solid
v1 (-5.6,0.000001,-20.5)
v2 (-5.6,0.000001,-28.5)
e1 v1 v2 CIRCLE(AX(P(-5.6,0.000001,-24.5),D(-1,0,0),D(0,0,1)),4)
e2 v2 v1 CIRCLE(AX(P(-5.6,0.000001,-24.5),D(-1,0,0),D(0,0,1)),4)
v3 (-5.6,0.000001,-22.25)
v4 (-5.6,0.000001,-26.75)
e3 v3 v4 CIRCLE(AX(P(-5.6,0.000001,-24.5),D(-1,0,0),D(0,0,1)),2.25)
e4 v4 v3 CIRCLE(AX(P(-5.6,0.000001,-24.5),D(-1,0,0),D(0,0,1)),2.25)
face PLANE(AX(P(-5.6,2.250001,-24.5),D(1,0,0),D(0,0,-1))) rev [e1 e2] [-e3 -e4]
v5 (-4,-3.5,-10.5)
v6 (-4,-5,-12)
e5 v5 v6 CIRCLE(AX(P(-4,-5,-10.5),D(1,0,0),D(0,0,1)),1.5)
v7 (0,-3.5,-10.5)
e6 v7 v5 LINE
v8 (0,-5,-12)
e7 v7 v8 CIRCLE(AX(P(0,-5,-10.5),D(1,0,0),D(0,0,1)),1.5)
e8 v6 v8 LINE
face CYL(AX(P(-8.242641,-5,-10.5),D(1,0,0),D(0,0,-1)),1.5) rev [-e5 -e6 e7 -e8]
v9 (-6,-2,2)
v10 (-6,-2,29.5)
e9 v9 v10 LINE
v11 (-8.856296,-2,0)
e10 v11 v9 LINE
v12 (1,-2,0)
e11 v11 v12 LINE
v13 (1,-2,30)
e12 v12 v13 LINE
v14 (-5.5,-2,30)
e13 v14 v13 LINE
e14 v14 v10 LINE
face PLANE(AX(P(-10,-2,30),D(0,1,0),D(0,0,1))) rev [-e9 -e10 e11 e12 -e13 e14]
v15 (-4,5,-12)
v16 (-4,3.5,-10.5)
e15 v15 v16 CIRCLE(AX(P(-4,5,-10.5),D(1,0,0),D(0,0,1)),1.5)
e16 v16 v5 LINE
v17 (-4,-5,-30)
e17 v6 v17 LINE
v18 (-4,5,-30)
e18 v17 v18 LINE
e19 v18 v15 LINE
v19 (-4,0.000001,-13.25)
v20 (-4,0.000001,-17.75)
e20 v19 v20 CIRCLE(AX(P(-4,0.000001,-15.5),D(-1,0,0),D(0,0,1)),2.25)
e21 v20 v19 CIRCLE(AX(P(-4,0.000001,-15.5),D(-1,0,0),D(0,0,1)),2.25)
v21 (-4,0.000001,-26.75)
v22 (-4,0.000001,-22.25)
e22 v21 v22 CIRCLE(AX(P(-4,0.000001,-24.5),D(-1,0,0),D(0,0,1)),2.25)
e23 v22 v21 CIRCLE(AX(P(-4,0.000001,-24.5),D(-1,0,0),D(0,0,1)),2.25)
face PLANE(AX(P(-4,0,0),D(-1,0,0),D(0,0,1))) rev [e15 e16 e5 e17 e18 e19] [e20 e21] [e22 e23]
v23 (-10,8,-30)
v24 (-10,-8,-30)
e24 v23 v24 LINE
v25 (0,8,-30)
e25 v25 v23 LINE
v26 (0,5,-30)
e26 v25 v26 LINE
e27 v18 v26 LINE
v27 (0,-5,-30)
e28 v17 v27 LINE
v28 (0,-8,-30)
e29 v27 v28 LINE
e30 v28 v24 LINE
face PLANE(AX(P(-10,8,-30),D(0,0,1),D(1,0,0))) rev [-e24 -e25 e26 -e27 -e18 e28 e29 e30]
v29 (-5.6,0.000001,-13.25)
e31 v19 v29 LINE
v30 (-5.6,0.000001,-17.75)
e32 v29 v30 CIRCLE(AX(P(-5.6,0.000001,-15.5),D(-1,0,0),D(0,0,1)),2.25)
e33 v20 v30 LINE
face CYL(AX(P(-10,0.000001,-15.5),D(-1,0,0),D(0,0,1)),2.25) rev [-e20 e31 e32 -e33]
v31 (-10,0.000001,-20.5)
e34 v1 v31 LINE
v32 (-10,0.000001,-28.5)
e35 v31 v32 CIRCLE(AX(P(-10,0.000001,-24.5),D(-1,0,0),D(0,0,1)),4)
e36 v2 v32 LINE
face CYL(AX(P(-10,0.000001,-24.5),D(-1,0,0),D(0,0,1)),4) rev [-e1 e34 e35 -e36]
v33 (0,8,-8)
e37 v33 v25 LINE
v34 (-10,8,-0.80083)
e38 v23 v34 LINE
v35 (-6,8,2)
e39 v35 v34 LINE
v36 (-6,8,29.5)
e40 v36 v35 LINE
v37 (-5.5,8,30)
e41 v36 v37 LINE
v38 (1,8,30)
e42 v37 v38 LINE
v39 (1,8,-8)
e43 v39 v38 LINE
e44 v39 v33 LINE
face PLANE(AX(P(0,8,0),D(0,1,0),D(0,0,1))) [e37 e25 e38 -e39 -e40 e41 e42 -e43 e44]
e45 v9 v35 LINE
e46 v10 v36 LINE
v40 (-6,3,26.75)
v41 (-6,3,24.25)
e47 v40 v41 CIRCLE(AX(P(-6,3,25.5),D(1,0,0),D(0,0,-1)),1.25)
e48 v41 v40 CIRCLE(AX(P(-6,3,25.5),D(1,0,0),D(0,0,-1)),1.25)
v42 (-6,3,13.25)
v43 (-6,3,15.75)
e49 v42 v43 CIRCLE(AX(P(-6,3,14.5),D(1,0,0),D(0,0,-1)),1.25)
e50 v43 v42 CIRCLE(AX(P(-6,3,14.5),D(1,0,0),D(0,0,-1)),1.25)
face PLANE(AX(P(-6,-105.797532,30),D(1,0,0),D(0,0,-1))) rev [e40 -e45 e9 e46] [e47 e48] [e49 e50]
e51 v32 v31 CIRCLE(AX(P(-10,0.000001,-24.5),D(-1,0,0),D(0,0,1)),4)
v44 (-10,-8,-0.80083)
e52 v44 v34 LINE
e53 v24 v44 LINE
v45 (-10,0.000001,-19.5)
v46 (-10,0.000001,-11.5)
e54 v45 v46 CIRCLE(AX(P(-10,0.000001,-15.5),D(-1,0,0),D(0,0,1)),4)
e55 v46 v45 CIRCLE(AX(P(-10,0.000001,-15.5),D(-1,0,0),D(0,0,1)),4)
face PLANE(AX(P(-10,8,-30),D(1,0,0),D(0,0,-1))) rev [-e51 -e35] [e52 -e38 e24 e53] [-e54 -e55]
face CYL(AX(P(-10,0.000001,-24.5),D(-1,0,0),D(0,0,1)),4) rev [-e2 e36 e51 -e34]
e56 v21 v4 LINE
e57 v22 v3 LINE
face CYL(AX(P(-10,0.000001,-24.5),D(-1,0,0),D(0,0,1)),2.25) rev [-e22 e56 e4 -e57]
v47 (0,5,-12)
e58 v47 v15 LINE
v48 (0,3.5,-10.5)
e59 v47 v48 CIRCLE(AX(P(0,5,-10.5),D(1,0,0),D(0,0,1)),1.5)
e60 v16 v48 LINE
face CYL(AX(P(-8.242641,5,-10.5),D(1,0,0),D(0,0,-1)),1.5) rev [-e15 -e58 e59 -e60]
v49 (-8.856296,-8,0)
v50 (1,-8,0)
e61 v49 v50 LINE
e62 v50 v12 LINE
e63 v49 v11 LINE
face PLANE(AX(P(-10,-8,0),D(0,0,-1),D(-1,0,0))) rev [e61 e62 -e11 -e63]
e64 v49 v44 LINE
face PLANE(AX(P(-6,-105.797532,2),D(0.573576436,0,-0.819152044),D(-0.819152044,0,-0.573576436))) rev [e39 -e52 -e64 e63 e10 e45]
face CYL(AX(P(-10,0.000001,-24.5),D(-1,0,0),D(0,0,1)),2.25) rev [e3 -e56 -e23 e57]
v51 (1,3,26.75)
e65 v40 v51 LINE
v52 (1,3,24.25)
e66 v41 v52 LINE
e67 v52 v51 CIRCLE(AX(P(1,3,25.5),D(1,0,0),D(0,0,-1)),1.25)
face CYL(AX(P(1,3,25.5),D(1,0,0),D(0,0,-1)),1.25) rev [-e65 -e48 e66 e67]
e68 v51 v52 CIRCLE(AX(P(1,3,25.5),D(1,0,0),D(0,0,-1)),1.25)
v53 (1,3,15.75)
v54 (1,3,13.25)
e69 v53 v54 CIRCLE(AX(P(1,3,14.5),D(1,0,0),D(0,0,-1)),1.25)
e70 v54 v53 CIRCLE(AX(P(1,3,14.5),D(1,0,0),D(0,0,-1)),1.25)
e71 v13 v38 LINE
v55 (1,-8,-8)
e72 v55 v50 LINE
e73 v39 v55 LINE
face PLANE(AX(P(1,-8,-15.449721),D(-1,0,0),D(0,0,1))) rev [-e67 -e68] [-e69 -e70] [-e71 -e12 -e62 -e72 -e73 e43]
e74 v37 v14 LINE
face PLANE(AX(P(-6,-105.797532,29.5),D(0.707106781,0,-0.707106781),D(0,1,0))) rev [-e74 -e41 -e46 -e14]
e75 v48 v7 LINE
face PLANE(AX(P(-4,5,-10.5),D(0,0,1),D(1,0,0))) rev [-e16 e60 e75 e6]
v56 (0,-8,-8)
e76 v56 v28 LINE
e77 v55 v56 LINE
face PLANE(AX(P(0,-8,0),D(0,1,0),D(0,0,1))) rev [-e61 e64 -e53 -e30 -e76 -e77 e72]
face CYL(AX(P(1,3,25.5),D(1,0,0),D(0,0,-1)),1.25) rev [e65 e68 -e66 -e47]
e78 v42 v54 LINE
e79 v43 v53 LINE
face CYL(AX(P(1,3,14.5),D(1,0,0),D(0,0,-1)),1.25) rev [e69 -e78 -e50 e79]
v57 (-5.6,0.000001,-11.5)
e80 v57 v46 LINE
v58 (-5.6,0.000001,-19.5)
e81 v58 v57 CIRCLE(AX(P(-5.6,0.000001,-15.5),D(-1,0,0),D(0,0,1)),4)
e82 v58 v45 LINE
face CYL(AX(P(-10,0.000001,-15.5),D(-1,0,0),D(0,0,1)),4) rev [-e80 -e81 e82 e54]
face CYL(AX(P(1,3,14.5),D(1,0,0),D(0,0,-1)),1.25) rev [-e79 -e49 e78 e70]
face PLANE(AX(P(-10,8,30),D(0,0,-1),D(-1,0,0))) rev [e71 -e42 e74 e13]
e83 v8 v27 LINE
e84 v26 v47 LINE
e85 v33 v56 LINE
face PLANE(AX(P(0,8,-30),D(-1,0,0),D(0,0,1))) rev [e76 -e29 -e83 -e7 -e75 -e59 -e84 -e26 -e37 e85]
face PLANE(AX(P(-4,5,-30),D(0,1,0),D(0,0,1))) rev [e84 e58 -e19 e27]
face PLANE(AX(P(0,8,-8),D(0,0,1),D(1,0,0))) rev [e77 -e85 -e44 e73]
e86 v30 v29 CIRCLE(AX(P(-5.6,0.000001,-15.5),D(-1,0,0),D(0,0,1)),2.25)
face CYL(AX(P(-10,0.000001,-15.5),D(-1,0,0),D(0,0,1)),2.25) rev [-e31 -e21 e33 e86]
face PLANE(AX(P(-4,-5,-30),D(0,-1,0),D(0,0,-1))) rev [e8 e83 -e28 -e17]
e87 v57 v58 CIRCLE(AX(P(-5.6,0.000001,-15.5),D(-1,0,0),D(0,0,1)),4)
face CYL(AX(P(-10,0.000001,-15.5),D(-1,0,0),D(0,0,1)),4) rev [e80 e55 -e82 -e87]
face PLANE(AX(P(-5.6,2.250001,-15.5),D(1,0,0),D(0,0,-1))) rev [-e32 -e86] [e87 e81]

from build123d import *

# Parameters (mm, degrees)
SKETCH_1_W                   = 20
SKETCH_1_H                   = 60
EXTRUDE_1_DEPTH              = 8
SKETCH_2_W                   = 19.5
SKETCH_2_H                   = 10
CUT_EXTRUDE_1_DEPTH          = 14
CHAMFER_1_SIZE               = 3
CUT_EXTRUDE_3_DEPTH          = 36.440090293
CUT_EXTRUDE_3_DEPTH_BACK     = 36.440090293
CHAMFER_2_SIZE               = 0.5
SKETCH_6_R                   = 1.5
CUT_EXTRUDE_4_DEPTH          = 14
HOLE_WIZARD_M4_1_D           = 4.5
HOLE_WIZARD_M4_1_CBORE_D     = 8
HOLE_WIZARD_M4_1_CBORE_DEPTH = 4.4
SKETCH_11_W                  = 10
SKETCH_11_H                  = 22
CUT_EXTRUDE_7_DEPTH          = 36.440090293
SKETCH_12_W                  = 30
SKETCH_12_H                  = 6
CUT_EXTRUDE_8_DEPTH          = 37.932370625
CUT_EXTRUDE_9_DEPTH          = 34.166247904
FILLET_2_R                   = 3
SKETCH_14_W                  = 18.511605667
SKETCH_14_H                  = 56.283608206
CUT_EXTRUDE_10_DEPTH         = 36.440090293
HOLE_WIZARD_M3_1_D           = 2.5


with BuildPart() as part:
    # 草图1 → 凸台-拉伸1 (new, symmetric)
    with BuildSketch(Plane(origin=(0, 0, 0), x_dir=(1, 0, 0), z_dir=(0, 1, 0))):
        Rectangle(SKETCH_1_W, SKETCH_1_H)
    extrude(amount=EXTRUDE_1_DEPTH, both=True)

    # 草图2 → 切除-拉伸1 (cut)
    with BuildSketch(Plane(origin=(10, 0, 0), x_dir=(0, 0, -1), z_dir=(1, 0, 0))):
        with Locations((20.25, 0)):
            Rectangle(SKETCH_2_W, SKETCH_2_H)
    extrude(amount=-CUT_EXTRUDE_1_DEPTH, mode=Mode.SUBTRACT)

    # 倒角1
    chamfer_1_edges = [part.edges().sort_by_distance(p)[0] for p in [
        (10, -6.5, -30),
        (10, 6.5, -30),
    ]]
    chamfer(chamfer_1_edges, length=CHAMFER_1_SIZE)

    # 草图5 → 切除-拉伸3 (cut, two sides: drawn at the far end of the back side and taken through both)
    with BuildSketch(Plane.XZ.offset(8).offset(-CUT_EXTRUDE_3_DEPTH_BACK)):
        Polygon((-6, 164.19339757), (-6, 30), (-6, 2), (-10, -0.800830153), (-119.92479595, -77.771000913), (-362.743295595, 36.555933952), (-248.818499645, 278.520332435), align=None)
    extrude(amount=CUT_EXTRUDE_3_DEPTH + CUT_EXTRUDE_3_DEPTH_BACK, mode=Mode.SUBTRACT)

    # 倒角2
    chamfer_2_edges = [part.edges().sort_by_distance(p)[0] for p in [
        (-6, 0, 30),
        (10, 0, 30),
    ]]
    chamfer(chamfer_2_edges, length=CHAMFER_2_SIZE)

    # 草图6 → 切除-拉伸4 (cut)
    with BuildSketch(Plane(origin=(10, 0, 0), x_dir=(0, 0, -1), z_dir=(1, 0, 0))):
        with Locations((10.5, 5)):
            Circle(SKETCH_6_R)
        with Locations((10.5, -5)):
            Circle(SKETCH_6_R)
    extrude(amount=-CUT_EXTRUDE_4_DEPTH, mode=Mode.SUBTRACT)

    # M4 六角凹头螺钉的柱形沉头孔1 (through all)
    with Locations(Plane.ZY.offset(10)):
        with Locations((-15.500000304, 6.53e-07), (-24.500000304, 6.53e-07)):
            CounterBoreHole(HOLE_WIZARD_M4_1_D / 2, HOLE_WIZARD_M4_1_CBORE_D / 2, HOLE_WIZARD_M4_1_CBORE_DEPTH)

    # 草图11 → 切除-拉伸7 (cut, through all)
    with BuildSketch(Plane.XZ.offset(8)):
        with Locations((5, -19)):
            Rectangle(SKETCH_11_W, SKETCH_11_H)
    extrude(amount=-CUT_EXTRUDE_7_DEPTH, mode=Mode.SUBTRACT)

    # 草图12 → 切除-拉伸8 (cut, through all)
    with BuildSketch(Plane(origin=(10, 0, 0), x_dir=(0, 0, -1), z_dir=(1, 0, 0))):
        with Locations((-15, -5)):
            Rectangle(SKETCH_12_W, SKETCH_12_H)
    extrude(amount=-CUT_EXTRUDE_8_DEPTH, mode=Mode.SUBTRACT)

    # 草图13 → 切除-拉伸9 (cut, through all)
    with BuildSketch(Plane.XZ.offset(2)):
        Polygon((10, 14.214190818), (5.948732796, 20), (10, 25.785809182), align=None)
    extrude(amount=-CUT_EXTRUDE_9_DEPTH, mode=Mode.SUBTRACT)

    # 圆角2
    fillet_2_edges = [part.edges().sort_by_distance(p)[0] for p in [
        (5.948732796, 3, 20),
    ]]
    fillet(fillet_2_edges, radius=FILLET_2_R)

    # 草图14 → 切除-拉伸10 (cut, through all)
    with BuildSketch(Plane(origin=(0, 8, 0), x_dir=(1, 0, 0), z_dir=(0, 1, 0))):
        with Locations((10.255802834, -12.692083527)):
            Rectangle(SKETCH_14_W, SKETCH_14_H)
    extrude(amount=-CUT_EXTRUDE_10_DEPTH, mode=Mode.SUBTRACT)

    # M3 螺纹孔1 (through all)
    with Locations(Plane(origin=(1, 0, 0), x_dir=(0, 0, -1), z_dir=(1, 0, 0))):
        with Locations((-25.5, 3), (-14.5, 3)):
            Hole(HOLE_WIZARD_M3_1_D / 2)


solid = part.part
